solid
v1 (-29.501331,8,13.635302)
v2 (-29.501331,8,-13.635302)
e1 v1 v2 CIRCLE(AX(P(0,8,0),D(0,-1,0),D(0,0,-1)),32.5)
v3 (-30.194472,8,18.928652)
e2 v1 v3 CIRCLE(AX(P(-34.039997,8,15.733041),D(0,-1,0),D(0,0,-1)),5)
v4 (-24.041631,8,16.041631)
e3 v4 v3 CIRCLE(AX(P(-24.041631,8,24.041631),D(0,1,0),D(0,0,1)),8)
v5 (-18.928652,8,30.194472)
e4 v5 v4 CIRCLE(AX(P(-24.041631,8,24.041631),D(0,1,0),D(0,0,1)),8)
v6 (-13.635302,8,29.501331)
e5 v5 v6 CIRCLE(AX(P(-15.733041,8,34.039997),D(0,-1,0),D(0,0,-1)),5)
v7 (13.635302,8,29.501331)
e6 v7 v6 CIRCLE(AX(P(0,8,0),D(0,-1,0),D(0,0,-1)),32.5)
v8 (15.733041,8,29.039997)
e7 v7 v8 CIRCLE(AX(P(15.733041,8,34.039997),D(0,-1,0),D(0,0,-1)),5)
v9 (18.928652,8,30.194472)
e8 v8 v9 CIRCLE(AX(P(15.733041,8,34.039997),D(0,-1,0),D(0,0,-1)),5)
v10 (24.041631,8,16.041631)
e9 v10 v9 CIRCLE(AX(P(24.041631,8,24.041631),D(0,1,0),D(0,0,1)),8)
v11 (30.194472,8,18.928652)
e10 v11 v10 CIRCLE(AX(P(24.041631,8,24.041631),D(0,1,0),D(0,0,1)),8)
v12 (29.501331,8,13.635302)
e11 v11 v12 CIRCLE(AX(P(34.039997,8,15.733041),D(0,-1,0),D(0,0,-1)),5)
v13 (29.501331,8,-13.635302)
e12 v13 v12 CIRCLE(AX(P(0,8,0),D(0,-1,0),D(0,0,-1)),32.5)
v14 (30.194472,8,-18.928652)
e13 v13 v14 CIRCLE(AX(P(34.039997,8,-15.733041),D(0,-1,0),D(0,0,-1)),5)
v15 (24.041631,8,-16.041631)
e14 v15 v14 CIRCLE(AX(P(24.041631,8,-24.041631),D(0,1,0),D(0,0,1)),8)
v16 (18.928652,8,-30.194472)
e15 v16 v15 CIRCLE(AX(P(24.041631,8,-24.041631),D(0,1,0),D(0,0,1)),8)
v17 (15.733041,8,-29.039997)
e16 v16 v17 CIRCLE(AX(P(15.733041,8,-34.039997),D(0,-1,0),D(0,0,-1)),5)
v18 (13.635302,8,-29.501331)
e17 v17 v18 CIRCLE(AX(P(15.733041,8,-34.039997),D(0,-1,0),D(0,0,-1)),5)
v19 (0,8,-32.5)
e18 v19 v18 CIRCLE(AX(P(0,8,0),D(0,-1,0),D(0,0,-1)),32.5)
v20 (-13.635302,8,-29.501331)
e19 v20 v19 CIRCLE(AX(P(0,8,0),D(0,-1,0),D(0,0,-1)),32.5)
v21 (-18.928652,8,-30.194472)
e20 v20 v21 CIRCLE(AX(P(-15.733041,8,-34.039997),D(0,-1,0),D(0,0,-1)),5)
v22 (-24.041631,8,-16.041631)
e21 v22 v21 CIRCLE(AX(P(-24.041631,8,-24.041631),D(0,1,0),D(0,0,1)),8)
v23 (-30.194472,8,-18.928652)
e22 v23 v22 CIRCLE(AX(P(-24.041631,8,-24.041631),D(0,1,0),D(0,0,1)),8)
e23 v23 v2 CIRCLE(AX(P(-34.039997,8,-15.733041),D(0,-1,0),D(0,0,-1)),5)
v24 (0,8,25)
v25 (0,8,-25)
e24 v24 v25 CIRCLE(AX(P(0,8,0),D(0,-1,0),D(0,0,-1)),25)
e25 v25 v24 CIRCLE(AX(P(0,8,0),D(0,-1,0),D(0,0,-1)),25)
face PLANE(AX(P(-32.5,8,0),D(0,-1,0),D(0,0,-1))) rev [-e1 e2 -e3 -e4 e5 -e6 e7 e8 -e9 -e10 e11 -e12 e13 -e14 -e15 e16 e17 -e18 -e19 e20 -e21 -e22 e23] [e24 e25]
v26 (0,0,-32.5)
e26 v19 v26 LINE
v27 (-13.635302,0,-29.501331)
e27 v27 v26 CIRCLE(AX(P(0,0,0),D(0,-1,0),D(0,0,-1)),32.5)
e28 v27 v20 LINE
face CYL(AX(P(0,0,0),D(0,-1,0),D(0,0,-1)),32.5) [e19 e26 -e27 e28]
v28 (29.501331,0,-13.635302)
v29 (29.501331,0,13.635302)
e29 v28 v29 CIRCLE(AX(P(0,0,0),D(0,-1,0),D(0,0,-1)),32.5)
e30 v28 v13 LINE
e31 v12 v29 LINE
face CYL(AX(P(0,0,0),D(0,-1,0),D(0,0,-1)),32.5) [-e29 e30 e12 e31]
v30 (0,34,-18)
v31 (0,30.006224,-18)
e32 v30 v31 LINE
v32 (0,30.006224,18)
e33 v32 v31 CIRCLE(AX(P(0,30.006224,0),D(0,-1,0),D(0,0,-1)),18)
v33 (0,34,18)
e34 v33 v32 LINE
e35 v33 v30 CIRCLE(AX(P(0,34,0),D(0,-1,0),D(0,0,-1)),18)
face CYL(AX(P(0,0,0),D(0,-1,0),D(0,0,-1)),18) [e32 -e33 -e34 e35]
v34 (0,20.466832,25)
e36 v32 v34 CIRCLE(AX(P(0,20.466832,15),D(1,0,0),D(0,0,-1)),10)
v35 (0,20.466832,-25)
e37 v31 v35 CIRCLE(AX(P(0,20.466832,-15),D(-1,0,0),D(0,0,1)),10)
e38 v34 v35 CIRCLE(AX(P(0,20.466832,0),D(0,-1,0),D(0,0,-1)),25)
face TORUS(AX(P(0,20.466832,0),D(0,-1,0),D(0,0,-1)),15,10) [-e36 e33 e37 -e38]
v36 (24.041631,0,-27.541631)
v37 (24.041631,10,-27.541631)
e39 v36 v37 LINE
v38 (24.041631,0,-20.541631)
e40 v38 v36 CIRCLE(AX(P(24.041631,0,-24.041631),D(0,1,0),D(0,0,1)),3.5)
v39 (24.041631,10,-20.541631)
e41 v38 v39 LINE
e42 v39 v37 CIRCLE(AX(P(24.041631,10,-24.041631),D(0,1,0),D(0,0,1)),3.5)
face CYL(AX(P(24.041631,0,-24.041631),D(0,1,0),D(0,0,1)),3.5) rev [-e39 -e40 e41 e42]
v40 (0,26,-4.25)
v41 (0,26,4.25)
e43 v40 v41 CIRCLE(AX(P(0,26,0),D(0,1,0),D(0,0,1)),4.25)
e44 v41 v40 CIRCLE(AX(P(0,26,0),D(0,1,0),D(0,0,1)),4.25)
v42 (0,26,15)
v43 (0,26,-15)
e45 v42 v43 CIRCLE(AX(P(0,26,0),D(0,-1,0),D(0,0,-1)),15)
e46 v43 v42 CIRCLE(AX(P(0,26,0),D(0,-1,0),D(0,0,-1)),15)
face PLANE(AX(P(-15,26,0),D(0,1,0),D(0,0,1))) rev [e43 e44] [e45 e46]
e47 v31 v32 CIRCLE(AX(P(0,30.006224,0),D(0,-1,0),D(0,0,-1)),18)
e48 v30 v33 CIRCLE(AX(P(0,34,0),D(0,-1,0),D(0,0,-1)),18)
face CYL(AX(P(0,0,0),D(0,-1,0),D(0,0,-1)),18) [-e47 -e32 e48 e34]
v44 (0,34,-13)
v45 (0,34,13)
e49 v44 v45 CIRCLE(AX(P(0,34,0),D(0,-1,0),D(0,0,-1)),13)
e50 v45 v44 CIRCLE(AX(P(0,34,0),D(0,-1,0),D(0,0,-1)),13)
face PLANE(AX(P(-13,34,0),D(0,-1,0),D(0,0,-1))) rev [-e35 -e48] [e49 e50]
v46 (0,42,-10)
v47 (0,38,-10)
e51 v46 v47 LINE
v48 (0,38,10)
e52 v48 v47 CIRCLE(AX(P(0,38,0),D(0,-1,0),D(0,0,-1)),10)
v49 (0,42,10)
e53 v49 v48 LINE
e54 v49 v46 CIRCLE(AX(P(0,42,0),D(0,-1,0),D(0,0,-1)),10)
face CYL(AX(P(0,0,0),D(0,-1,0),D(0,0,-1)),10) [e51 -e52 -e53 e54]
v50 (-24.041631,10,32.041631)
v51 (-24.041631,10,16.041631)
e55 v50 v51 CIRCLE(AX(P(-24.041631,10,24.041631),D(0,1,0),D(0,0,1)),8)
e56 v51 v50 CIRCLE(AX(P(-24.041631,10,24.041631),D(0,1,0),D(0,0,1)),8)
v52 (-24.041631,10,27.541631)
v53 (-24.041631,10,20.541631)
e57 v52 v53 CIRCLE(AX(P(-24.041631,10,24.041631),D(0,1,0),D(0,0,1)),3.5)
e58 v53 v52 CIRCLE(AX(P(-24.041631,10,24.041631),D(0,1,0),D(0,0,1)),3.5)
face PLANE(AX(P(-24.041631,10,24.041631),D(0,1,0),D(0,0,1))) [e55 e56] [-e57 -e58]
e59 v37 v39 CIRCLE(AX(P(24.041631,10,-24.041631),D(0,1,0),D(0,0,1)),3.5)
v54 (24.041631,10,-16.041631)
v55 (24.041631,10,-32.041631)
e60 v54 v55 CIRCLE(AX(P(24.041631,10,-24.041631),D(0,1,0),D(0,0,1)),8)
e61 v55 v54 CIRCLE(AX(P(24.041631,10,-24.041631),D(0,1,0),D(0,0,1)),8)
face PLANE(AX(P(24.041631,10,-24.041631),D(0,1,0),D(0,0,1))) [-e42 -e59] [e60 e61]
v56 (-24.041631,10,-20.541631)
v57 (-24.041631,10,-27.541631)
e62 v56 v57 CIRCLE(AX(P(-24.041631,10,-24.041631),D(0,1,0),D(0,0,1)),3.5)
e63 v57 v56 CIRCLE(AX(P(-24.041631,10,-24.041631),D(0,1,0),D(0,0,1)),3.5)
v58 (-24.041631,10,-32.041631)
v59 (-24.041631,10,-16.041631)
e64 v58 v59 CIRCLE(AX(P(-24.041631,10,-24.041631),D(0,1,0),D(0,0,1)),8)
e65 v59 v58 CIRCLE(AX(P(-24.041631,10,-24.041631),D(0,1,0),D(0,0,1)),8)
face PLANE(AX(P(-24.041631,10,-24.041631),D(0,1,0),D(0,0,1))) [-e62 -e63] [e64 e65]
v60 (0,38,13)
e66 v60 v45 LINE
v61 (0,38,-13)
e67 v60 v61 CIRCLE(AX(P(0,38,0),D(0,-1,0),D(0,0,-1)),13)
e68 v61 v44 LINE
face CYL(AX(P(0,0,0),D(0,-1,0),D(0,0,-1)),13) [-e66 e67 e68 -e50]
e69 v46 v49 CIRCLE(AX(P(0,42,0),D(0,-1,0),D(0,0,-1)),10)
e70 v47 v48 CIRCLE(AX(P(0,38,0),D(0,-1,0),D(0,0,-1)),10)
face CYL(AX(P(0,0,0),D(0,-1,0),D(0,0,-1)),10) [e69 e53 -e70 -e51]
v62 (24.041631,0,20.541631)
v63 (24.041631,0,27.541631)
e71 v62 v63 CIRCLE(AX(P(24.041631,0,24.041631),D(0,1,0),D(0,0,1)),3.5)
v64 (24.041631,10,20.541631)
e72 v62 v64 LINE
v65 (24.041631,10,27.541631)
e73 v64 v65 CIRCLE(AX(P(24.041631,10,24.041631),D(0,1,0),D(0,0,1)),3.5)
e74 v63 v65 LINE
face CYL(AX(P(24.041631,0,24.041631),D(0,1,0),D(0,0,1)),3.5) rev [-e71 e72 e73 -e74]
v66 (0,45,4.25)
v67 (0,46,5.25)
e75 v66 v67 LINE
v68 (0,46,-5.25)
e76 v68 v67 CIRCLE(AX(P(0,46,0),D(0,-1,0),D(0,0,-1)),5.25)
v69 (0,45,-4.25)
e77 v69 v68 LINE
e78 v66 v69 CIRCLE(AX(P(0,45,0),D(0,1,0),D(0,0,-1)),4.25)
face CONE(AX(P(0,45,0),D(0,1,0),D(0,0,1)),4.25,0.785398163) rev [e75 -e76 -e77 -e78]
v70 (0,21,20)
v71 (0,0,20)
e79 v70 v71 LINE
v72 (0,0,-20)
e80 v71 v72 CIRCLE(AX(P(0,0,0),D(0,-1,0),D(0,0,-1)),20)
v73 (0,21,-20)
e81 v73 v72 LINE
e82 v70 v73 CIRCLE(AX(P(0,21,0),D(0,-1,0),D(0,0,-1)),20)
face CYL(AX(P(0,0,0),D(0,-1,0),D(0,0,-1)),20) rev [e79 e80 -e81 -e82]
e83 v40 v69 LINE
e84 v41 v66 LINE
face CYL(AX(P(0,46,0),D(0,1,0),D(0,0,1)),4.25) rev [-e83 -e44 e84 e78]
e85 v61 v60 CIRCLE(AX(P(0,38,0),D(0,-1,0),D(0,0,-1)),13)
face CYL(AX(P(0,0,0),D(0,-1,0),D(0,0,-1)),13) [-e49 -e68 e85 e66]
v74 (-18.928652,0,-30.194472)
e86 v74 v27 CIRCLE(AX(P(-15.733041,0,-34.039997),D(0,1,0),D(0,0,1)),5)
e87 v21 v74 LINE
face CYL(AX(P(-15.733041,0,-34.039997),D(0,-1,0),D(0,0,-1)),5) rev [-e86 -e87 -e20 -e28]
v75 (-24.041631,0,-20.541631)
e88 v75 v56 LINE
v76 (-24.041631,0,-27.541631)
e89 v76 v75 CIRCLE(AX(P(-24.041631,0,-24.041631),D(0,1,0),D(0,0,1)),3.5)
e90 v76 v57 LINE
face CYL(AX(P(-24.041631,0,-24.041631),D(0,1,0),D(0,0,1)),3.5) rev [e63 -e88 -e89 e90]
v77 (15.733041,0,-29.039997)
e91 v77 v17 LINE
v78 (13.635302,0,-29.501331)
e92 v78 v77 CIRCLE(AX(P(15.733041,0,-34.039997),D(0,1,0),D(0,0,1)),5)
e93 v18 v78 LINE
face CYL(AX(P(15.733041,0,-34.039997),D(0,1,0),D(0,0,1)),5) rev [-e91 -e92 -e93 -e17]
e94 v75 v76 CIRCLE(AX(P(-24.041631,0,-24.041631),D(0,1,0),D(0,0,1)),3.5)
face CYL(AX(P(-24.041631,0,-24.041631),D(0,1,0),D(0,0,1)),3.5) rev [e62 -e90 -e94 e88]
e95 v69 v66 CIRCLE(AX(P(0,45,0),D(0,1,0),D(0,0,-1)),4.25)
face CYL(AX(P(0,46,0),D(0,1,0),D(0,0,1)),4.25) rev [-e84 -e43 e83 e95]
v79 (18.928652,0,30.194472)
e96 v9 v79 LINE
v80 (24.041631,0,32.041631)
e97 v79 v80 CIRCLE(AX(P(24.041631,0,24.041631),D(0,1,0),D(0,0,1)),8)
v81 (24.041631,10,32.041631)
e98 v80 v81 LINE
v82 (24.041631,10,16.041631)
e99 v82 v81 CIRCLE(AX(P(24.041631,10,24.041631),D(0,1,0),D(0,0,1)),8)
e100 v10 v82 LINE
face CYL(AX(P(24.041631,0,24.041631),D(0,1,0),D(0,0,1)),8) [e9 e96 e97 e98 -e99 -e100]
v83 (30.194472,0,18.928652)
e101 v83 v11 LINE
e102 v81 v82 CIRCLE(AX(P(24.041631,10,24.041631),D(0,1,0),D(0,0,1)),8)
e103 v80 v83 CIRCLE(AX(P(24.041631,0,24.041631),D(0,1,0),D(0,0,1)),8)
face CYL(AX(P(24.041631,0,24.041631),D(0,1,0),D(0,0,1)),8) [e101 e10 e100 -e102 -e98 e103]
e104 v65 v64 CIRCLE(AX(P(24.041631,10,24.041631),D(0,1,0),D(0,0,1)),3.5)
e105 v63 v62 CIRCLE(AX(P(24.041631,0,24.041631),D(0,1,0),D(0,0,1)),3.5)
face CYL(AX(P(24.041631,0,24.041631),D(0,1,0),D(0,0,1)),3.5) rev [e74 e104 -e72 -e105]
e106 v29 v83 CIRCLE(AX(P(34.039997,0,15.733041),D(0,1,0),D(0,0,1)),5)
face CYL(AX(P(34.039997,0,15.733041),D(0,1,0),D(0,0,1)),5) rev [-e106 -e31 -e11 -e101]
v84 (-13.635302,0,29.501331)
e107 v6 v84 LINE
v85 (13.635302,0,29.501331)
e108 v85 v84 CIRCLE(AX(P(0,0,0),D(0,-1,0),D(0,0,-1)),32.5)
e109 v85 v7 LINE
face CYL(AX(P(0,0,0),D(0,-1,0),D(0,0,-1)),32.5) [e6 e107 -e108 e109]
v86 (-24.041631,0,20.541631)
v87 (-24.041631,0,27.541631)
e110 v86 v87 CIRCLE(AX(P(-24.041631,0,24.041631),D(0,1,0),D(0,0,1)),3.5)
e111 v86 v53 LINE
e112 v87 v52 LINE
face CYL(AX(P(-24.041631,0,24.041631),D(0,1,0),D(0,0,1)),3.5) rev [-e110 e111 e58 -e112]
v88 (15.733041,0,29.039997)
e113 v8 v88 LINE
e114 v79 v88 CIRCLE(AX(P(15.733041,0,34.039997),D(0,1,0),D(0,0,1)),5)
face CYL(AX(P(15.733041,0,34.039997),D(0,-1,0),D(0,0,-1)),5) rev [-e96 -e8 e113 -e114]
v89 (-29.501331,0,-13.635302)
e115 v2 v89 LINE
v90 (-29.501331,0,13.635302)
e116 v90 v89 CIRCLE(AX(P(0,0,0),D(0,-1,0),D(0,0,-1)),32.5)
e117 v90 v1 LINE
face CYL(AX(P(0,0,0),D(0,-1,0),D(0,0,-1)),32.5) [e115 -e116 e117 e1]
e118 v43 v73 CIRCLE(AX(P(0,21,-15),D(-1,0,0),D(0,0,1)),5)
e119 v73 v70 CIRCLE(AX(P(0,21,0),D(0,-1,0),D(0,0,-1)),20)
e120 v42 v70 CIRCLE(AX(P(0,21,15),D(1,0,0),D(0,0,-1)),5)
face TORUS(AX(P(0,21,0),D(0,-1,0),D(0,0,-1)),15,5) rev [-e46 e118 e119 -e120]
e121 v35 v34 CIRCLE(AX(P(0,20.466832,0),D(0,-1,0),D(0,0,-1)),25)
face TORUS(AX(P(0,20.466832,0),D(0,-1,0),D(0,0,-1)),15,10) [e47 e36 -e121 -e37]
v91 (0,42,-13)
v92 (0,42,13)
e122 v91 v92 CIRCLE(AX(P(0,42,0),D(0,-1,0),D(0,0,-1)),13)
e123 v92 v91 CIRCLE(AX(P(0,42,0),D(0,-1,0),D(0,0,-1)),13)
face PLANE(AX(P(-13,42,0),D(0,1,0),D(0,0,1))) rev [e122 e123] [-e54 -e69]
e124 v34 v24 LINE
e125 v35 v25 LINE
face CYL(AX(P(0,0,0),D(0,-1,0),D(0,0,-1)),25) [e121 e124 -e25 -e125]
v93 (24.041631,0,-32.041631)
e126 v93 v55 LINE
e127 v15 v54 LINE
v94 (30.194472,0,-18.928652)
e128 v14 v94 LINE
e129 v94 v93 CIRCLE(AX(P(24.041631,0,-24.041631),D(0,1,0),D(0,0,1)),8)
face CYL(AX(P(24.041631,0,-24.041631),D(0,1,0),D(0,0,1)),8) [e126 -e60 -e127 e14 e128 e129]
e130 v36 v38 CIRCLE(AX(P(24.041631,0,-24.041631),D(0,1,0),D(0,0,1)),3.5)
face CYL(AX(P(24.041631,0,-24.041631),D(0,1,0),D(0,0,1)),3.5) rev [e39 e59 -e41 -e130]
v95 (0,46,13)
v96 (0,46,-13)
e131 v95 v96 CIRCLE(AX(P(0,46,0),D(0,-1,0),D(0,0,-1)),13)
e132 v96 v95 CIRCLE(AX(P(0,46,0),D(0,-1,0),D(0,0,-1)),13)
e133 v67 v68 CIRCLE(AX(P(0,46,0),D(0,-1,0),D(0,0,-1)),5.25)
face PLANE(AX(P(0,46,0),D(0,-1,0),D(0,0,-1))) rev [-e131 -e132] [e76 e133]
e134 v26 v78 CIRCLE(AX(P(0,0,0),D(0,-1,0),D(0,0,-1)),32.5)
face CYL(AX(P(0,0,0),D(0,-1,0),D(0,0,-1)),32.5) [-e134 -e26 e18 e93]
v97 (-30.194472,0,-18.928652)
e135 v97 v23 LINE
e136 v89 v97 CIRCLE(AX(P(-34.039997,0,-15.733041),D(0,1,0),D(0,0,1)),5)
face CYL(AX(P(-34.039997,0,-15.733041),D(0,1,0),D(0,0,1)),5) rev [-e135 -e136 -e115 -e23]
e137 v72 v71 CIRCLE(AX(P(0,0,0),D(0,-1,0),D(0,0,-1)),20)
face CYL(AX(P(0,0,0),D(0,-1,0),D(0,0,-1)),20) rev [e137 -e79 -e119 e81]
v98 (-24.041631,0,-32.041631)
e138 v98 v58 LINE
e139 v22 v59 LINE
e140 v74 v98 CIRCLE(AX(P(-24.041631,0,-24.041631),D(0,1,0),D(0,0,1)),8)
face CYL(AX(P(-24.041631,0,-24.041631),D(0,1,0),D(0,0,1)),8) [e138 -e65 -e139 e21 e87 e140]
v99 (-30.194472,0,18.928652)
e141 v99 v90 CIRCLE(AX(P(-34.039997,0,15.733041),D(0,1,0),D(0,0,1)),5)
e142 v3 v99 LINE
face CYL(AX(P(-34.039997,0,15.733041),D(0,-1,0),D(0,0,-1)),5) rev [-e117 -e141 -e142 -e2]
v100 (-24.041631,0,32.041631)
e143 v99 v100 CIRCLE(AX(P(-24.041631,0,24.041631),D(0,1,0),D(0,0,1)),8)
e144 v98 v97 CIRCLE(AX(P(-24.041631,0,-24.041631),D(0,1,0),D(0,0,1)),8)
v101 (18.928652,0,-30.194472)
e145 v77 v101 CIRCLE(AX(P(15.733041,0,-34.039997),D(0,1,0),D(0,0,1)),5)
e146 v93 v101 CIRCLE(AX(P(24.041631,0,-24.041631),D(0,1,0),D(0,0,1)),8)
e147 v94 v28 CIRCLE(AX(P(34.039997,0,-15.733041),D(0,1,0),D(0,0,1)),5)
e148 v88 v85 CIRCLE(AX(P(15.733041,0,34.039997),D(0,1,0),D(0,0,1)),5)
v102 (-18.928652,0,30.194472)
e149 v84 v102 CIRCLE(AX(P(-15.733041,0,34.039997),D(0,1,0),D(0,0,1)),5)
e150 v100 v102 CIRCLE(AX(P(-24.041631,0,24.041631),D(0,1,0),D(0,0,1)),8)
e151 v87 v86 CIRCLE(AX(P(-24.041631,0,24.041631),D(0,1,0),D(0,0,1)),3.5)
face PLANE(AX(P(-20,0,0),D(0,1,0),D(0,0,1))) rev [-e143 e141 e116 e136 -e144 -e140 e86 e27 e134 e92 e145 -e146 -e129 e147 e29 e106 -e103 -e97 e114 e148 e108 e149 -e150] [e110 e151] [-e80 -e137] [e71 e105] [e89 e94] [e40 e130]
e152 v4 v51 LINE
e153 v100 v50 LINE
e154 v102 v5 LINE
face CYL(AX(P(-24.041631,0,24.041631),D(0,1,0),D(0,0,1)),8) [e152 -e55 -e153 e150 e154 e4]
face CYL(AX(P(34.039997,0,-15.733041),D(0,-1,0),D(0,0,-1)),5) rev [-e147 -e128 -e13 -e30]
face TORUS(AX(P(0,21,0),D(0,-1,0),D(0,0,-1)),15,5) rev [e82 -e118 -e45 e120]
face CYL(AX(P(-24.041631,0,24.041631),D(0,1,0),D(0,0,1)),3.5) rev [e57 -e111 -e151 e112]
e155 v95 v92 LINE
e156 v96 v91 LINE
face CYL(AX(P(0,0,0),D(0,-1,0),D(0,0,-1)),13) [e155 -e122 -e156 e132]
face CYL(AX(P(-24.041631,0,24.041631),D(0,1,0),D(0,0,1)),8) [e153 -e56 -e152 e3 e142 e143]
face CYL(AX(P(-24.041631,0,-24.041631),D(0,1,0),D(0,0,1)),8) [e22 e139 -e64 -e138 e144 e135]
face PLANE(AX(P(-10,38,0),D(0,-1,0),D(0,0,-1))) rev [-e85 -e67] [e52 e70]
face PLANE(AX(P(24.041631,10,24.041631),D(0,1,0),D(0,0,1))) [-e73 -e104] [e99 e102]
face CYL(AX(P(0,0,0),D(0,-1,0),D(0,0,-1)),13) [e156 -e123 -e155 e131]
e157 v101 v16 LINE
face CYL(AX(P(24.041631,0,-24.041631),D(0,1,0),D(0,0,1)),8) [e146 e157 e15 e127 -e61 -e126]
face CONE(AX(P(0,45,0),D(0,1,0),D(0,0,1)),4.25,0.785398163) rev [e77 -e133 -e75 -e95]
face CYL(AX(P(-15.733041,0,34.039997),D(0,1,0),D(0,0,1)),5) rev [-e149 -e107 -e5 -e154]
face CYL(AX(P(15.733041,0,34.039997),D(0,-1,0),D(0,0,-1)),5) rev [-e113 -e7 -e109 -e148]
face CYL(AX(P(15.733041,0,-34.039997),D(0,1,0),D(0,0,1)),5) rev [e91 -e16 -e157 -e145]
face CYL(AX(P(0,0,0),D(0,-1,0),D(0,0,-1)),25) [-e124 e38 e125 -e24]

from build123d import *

# Parameters (mm, degrees)
M10_TAPPED_HOLE1_D  = 8.5
CHAMFER1_SIZE       = 1
SKETCH6_R           = 8
SKETCH6_R_2         = 3.5
BOSS_EXTRUDE1_DEPTH = 8
SKETCH7_R           = 3.5
CUT_EXTRUDE1_DEPTH  = 8
FILLET1_R           = 5
BOSS_EXTRUDE2_START = 2
SKETCH8_R           = 8
SKETCH8_R_2         = 3.5
BOSS_EXTRUDE2_DEPTH = 2


with BuildPart() as part:
    # Sketch1 → Revolve1 (revolve)
    with BuildSketch(Plane.XY, mode=Mode.PRIVATE) as revolve1_sk:
        with BuildLine():
            Line((0, 46), (-13, 46))
            Line((-13, 46), (-13, 42))
            Line((-13, 42), (-10, 42))
            Line((-10, 42), (-10, 38))
            Line((-10, 38), (-13, 38))
            Line((-13, 38), (-13, 34))
            Line((-13, 34), (-18, 34))
            Line((-18, 34), (-18, 30.006223624))
            ThreePointArc((-18, 30.006223624), (-23.062257748, 26.382911393), (-25, 20.46683161))
            Line((-25, 20.46683161), (-25, 8))
            Line((-25, 8), (-32.5, 8))
            Line((-32.5, 8), (-32.5, 0))
            Line((-32.5, 0), (-20, 0))
            Line((-20, 0), (-20, 21))
            ThreePointArc((-20, 21), (-18.535533906, 24.535533906), (-15, 26))
            Line((-15, 26), (0, 26))
            Line((0, 26), (0, 46))
        make_face()
    revolve(revolve1_sk.sketch.rotate(Axis((0, 0, 0), (0, 1, 0)), 270), axis=Axis((0, 0, 0), (0, 1, 0)))

    # M10 Tapped Hole1 (through all)
    with Locations(Plane(origin=(0, 46, 0), x_dir=(1, 0, 0), z_dir=(0, 1, 0))):
        with Locations((0, 0)):
            Hole(M10_TAPPED_HOLE1_D / 2)

    # Chamfer1
    chamfer1_edges = [part.edges().sort_by_distance(p)[0] for p in [
        (4.25, 46, 0),
    ]]
    chamfer(chamfer1_edges, length=CHAMFER1_SIZE)

    # Sketch6 → Boss-Extrude1 (add)
    # profile 1 of 4: a face of its own
    with BuildSketch(Plane(origin=(0, 8, 0), x_dir=(1, 0, 0), z_dir=(0, 1, 0))):
        with Locations((-24.04163056, 24.04163056)):
            Circle(SKETCH6_R)
        with Locations((-24.04163056, 24.04163056)):
            Circle(SKETCH6_R_2, mode=Mode.SUBTRACT)
    # profile 2 of 4: a face of its own
    with BuildSketch(Plane(origin=(0, 8, 0), x_dir=(1, 0, 0), z_dir=(0, 1, 0))):
        with Locations((24.04163056, 24.04163056)):
            Circle(SKETCH6_R)
        with Locations((24.04163056, 24.04163056)):
            Circle(SKETCH6_R_2, mode=Mode.SUBTRACT)
    # profile 3 of 4: a face of its own
    with BuildSketch(Plane(origin=(0, 8, 0), x_dir=(1, 0, 0), z_dir=(0, 1, 0))):
        with Locations((24.04163056, -24.04163056)):
            Circle(SKETCH6_R)
        with Locations((24.04163056, -24.04163056)):
            Circle(SKETCH6_R_2, mode=Mode.SUBTRACT)
    # profile 4 of 4: a face of its own
    with BuildSketch(Plane(origin=(0, 8, 0), x_dir=(1, 0, 0), z_dir=(0, 1, 0))):
        with Locations((-24.04163056, -24.04163056)):
            Circle(SKETCH6_R)
        with Locations((-24.04163056, -24.04163056)):
            Circle(SKETCH6_R_2, mode=Mode.SUBTRACT)
    extrude(amount=-BOSS_EXTRUDE1_DEPTH)

    # Sketch7 → Cut-Extrude1 (cut)
    with BuildSketch(Plane(origin=(0, 8, 0), x_dir=(1, 0, 0), z_dir=(0, 1, 0))):
        with Locations(Location((-24.04163056, 24.04163056, 0), (0, 0, 270))):
            Circle(SKETCH7_R)
        with Locations(Location((24.04163056, 24.04163056, 0), (0, 0, 270))):
            Circle(SKETCH7_R)
        with Locations(Location((24.04163056, -24.04163056, 0), (0, 0, 270))):
            Circle(SKETCH7_R)
        with Locations(Location((-24.04163056, -24.04163056, 0), (0, 0, 270))):
            Circle(SKETCH7_R)
    extrude(amount=-CUT_EXTRUDE1_DEPTH, mode=Mode.SUBTRACT)

    # Fillet1
    fillet1_edges = [part.edges().sort_by_distance(p)[0] for p in [
        (-16.944361965, 4, -27.733348113),
        (-27.733348113, 4, -16.944361965),
        (-27.733348113, 4, 16.944361965),
        (-16.944361965, 4, 27.733348113),
        (16.944361965, 4, 27.733348113),
        (27.733348113, 4, 16.944361965),
        (27.733348113, 4, -16.944361965),
        (16.944361965, 4, -27.733348113),
    ]]
    fillet(fillet1_edges, radius=FILLET1_R)

    # Sketch8 → Boss-Extrude2 (add)
    # profile 1 of 4: a face of its own
    with BuildSketch(Plane(origin=(0, 8, 0), x_dir=(1, 0, 0), z_dir=(0, 1, 0)).offset(BOSS_EXTRUDE2_START)):
        with Locations(Location((-24.04163056, 24.04163056, 0), (0, 0, 270))):
            Circle(SKETCH8_R)
        with Locations(Location((-24.04163056, 24.04163056, 0), (0, 0, 270))):
            Circle(SKETCH8_R_2, mode=Mode.SUBTRACT)
    # profile 2 of 4: a face of its own
    with BuildSketch(Plane(origin=(0, 8, 0), x_dir=(1, 0, 0), z_dir=(0, 1, 0)).offset(BOSS_EXTRUDE2_START)):
        with Locations(Location((24.04163056, 24.04163056, 0), (0, 0, 270))):
            Circle(SKETCH8_R)
        with Locations(Location((24.04163056, 24.04163056, 0), (0, 0, 270))):
            Circle(SKETCH8_R_2, mode=Mode.SUBTRACT)
    # profile 3 of 4: a face of its own
    with BuildSketch(Plane(origin=(0, 8, 0), x_dir=(1, 0, 0), z_dir=(0, 1, 0)).offset(BOSS_EXTRUDE2_START)):
        with Locations(Location((24.04163056, -24.04163056, 0), (0, 0, 270))):
            Circle(SKETCH8_R)
        with Locations(Location((24.04163056, -24.04163056, 0), (0, 0, 270))):
            Circle(SKETCH8_R_2, mode=Mode.SUBTRACT)
    # profile 4 of 4: a face of its own
    with BuildSketch(Plane(origin=(0, 8, 0), x_dir=(1, 0, 0), z_dir=(0, 1, 0)).offset(BOSS_EXTRUDE2_START)):
        with Locations(Location((-24.04163056, -24.04163056, 0), (0, 0, 270))):
            Circle(SKETCH8_R)
        with Locations(Location((-24.04163056, -24.04163056, 0), (0, 0, 270))):
            Circle(SKETCH8_R_2, mode=Mode.SUBTRACT)
    extrude(amount=-BOSS_EXTRUDE2_DEPTH)


solid = part.part
